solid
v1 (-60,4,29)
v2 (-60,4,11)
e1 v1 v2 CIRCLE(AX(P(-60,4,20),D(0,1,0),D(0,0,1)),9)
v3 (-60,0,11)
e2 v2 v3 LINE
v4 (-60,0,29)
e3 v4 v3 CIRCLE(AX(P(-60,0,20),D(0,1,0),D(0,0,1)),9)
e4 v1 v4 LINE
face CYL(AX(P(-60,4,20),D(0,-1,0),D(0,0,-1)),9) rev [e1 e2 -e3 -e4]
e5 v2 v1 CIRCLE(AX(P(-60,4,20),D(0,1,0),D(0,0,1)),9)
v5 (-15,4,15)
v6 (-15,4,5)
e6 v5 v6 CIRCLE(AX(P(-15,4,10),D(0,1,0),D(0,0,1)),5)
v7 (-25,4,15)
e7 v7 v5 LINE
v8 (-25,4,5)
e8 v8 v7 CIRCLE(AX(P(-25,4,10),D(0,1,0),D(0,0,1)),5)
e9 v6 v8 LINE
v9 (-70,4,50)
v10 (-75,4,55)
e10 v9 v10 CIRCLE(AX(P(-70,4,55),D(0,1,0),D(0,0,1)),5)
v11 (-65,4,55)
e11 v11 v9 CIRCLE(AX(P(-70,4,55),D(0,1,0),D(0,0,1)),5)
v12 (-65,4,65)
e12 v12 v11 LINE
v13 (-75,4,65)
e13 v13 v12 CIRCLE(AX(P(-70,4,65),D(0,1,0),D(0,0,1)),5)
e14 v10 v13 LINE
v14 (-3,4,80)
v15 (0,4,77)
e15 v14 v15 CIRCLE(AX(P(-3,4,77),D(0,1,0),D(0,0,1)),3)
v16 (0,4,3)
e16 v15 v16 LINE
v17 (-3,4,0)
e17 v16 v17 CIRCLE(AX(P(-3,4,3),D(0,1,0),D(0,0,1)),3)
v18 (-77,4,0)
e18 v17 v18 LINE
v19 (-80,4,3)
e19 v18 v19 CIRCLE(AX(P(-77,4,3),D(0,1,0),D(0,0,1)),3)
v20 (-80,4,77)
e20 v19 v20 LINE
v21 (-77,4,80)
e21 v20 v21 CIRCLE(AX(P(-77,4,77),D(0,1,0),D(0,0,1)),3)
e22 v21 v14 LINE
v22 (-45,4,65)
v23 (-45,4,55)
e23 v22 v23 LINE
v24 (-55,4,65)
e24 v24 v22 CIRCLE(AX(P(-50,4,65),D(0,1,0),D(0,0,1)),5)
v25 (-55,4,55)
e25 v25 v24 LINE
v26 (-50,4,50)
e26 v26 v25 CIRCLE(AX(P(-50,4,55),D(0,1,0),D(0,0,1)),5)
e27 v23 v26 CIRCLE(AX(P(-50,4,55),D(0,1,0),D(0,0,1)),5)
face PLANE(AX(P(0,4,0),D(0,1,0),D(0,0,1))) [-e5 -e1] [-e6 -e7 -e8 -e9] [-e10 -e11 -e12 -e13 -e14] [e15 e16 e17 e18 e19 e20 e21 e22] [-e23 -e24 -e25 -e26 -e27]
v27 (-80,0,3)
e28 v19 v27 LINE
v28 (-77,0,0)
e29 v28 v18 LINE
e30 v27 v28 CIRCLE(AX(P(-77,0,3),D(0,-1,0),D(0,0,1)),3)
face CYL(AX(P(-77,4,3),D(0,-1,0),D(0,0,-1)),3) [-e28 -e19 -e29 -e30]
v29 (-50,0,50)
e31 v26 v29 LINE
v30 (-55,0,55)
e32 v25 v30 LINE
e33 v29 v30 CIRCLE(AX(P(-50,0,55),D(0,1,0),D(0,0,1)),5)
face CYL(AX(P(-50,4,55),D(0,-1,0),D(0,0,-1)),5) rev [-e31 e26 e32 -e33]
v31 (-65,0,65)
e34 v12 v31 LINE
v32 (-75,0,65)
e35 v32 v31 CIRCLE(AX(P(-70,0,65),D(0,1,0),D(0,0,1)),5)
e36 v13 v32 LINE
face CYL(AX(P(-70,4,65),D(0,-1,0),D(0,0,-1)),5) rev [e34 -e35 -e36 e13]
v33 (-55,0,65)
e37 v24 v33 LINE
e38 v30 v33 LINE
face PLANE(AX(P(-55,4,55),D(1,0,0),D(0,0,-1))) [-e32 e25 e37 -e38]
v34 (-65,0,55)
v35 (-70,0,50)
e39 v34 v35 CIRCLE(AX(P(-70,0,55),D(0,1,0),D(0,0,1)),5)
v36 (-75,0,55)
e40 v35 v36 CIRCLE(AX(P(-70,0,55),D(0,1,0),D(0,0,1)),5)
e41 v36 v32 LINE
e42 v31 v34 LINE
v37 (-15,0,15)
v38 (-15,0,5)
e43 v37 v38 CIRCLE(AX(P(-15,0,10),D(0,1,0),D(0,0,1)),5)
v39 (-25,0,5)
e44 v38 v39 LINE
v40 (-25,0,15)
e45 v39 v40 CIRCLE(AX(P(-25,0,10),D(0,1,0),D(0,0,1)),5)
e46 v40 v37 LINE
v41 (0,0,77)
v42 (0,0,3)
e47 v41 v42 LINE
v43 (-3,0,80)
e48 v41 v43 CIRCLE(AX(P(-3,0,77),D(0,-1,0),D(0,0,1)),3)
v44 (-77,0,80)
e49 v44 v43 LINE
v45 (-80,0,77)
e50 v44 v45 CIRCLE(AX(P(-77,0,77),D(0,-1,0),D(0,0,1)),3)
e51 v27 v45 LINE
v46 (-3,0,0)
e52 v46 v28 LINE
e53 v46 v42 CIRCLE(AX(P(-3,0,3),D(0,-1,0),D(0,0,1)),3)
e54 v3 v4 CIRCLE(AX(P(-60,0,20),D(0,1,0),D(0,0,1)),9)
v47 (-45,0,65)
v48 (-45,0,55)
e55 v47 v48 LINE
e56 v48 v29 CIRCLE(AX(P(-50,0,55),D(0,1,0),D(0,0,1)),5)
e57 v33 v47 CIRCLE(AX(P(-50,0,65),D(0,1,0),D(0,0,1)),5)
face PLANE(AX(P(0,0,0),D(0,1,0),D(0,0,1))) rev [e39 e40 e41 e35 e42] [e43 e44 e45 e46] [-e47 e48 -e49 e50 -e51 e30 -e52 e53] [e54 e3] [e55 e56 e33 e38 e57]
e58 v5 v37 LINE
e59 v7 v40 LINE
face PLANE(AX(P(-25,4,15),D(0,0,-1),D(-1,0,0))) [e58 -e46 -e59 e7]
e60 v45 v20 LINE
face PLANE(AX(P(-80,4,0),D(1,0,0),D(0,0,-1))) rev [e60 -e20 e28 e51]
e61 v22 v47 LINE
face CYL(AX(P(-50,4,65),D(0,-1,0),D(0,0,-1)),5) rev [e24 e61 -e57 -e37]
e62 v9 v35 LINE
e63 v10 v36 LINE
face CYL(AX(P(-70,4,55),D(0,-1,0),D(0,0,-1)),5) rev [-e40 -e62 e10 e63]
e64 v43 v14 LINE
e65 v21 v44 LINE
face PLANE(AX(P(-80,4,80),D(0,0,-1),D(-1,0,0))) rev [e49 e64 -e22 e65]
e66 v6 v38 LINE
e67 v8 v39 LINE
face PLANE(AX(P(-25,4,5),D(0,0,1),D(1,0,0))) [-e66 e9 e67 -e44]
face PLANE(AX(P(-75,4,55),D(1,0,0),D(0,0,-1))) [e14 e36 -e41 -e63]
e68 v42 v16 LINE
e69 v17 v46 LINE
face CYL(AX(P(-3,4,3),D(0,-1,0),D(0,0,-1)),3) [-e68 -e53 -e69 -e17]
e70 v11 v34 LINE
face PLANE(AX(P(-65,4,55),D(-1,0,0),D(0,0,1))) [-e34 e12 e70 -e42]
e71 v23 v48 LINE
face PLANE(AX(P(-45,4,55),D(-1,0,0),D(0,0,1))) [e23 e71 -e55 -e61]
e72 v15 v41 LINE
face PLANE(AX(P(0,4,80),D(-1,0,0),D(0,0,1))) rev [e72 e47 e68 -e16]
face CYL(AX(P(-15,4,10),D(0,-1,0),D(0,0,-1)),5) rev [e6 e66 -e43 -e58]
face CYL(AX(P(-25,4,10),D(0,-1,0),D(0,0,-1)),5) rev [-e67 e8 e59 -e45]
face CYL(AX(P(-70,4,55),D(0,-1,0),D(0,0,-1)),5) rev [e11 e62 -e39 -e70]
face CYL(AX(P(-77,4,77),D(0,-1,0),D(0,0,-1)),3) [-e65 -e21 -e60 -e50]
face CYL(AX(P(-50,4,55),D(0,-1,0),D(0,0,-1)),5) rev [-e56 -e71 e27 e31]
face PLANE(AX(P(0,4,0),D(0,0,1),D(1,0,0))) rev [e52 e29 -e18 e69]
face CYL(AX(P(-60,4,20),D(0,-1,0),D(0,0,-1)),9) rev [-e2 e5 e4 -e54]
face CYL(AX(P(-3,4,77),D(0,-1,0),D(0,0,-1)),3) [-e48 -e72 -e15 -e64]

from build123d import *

# Parameters (mm, degrees)
SKETCH1_W           = 80
SKETCH1_H           = 80
SKETCH1_R           = 9
BOSS_EXTRUDE1_DEPTH = 4
FILLET1_R           = 3


with BuildPart() as part:
    # Sketch1 → Boss-Extrude1 (new body)
    with BuildSketch(Plane(origin=(0, 0, 0), x_dir=(1, 0, 0), z_dir=(0, 1, 0))):
        with Locations((-40, -40)):
            Rectangle(SKETCH1_W, SKETCH1_H)
        with Locations(Location((-60, -20, 0), (0, 0, 270))):
            Circle(SKETCH1_R, mode=Mode.SUBTRACT)
        with BuildLine():
            Line((-25, -5), (-15, -5))
            ThreePointArc((-15, -5), (-10, -10), (-15, -15))
            Line((-15, -15), (-25, -15))
            ThreePointArc((-25, -15), (-30, -10), (-25, -5))
        make_face(mode=Mode.SUBTRACT)
        with BuildLine():
            Line((-65, -55), (-65, -65))
            ThreePointArc((-65, -65), (-70, -70), (-75, -65))
            Line((-75, -65), (-75, -55))
            ThreePointArc((-75, -55), (-70, -50), (-65, -55))
        make_face(mode=Mode.SUBTRACT)
        with BuildLine():
            Line((-45, -55), (-45, -65))
            ThreePointArc((-45, -65), (-50, -70), (-55, -65))
            Line((-55, -65), (-55, -55))
            ThreePointArc((-55, -55), (-50, -50), (-45, -55))
        make_face(mode=Mode.SUBTRACT)
    extrude(amount=BOSS_EXTRUDE1_DEPTH)

    # Fillet1
    fillet1_edges = [part.edges().sort_by_distance(p)[0] for p in [
        (0, 2, 80),
        (-80, 2, 80),
        (-80, 2, 0),
        (0, 2, 0),
    ]]
    fillet(fillet1_edges, radius=FILLET1_R)


solid = part.part
